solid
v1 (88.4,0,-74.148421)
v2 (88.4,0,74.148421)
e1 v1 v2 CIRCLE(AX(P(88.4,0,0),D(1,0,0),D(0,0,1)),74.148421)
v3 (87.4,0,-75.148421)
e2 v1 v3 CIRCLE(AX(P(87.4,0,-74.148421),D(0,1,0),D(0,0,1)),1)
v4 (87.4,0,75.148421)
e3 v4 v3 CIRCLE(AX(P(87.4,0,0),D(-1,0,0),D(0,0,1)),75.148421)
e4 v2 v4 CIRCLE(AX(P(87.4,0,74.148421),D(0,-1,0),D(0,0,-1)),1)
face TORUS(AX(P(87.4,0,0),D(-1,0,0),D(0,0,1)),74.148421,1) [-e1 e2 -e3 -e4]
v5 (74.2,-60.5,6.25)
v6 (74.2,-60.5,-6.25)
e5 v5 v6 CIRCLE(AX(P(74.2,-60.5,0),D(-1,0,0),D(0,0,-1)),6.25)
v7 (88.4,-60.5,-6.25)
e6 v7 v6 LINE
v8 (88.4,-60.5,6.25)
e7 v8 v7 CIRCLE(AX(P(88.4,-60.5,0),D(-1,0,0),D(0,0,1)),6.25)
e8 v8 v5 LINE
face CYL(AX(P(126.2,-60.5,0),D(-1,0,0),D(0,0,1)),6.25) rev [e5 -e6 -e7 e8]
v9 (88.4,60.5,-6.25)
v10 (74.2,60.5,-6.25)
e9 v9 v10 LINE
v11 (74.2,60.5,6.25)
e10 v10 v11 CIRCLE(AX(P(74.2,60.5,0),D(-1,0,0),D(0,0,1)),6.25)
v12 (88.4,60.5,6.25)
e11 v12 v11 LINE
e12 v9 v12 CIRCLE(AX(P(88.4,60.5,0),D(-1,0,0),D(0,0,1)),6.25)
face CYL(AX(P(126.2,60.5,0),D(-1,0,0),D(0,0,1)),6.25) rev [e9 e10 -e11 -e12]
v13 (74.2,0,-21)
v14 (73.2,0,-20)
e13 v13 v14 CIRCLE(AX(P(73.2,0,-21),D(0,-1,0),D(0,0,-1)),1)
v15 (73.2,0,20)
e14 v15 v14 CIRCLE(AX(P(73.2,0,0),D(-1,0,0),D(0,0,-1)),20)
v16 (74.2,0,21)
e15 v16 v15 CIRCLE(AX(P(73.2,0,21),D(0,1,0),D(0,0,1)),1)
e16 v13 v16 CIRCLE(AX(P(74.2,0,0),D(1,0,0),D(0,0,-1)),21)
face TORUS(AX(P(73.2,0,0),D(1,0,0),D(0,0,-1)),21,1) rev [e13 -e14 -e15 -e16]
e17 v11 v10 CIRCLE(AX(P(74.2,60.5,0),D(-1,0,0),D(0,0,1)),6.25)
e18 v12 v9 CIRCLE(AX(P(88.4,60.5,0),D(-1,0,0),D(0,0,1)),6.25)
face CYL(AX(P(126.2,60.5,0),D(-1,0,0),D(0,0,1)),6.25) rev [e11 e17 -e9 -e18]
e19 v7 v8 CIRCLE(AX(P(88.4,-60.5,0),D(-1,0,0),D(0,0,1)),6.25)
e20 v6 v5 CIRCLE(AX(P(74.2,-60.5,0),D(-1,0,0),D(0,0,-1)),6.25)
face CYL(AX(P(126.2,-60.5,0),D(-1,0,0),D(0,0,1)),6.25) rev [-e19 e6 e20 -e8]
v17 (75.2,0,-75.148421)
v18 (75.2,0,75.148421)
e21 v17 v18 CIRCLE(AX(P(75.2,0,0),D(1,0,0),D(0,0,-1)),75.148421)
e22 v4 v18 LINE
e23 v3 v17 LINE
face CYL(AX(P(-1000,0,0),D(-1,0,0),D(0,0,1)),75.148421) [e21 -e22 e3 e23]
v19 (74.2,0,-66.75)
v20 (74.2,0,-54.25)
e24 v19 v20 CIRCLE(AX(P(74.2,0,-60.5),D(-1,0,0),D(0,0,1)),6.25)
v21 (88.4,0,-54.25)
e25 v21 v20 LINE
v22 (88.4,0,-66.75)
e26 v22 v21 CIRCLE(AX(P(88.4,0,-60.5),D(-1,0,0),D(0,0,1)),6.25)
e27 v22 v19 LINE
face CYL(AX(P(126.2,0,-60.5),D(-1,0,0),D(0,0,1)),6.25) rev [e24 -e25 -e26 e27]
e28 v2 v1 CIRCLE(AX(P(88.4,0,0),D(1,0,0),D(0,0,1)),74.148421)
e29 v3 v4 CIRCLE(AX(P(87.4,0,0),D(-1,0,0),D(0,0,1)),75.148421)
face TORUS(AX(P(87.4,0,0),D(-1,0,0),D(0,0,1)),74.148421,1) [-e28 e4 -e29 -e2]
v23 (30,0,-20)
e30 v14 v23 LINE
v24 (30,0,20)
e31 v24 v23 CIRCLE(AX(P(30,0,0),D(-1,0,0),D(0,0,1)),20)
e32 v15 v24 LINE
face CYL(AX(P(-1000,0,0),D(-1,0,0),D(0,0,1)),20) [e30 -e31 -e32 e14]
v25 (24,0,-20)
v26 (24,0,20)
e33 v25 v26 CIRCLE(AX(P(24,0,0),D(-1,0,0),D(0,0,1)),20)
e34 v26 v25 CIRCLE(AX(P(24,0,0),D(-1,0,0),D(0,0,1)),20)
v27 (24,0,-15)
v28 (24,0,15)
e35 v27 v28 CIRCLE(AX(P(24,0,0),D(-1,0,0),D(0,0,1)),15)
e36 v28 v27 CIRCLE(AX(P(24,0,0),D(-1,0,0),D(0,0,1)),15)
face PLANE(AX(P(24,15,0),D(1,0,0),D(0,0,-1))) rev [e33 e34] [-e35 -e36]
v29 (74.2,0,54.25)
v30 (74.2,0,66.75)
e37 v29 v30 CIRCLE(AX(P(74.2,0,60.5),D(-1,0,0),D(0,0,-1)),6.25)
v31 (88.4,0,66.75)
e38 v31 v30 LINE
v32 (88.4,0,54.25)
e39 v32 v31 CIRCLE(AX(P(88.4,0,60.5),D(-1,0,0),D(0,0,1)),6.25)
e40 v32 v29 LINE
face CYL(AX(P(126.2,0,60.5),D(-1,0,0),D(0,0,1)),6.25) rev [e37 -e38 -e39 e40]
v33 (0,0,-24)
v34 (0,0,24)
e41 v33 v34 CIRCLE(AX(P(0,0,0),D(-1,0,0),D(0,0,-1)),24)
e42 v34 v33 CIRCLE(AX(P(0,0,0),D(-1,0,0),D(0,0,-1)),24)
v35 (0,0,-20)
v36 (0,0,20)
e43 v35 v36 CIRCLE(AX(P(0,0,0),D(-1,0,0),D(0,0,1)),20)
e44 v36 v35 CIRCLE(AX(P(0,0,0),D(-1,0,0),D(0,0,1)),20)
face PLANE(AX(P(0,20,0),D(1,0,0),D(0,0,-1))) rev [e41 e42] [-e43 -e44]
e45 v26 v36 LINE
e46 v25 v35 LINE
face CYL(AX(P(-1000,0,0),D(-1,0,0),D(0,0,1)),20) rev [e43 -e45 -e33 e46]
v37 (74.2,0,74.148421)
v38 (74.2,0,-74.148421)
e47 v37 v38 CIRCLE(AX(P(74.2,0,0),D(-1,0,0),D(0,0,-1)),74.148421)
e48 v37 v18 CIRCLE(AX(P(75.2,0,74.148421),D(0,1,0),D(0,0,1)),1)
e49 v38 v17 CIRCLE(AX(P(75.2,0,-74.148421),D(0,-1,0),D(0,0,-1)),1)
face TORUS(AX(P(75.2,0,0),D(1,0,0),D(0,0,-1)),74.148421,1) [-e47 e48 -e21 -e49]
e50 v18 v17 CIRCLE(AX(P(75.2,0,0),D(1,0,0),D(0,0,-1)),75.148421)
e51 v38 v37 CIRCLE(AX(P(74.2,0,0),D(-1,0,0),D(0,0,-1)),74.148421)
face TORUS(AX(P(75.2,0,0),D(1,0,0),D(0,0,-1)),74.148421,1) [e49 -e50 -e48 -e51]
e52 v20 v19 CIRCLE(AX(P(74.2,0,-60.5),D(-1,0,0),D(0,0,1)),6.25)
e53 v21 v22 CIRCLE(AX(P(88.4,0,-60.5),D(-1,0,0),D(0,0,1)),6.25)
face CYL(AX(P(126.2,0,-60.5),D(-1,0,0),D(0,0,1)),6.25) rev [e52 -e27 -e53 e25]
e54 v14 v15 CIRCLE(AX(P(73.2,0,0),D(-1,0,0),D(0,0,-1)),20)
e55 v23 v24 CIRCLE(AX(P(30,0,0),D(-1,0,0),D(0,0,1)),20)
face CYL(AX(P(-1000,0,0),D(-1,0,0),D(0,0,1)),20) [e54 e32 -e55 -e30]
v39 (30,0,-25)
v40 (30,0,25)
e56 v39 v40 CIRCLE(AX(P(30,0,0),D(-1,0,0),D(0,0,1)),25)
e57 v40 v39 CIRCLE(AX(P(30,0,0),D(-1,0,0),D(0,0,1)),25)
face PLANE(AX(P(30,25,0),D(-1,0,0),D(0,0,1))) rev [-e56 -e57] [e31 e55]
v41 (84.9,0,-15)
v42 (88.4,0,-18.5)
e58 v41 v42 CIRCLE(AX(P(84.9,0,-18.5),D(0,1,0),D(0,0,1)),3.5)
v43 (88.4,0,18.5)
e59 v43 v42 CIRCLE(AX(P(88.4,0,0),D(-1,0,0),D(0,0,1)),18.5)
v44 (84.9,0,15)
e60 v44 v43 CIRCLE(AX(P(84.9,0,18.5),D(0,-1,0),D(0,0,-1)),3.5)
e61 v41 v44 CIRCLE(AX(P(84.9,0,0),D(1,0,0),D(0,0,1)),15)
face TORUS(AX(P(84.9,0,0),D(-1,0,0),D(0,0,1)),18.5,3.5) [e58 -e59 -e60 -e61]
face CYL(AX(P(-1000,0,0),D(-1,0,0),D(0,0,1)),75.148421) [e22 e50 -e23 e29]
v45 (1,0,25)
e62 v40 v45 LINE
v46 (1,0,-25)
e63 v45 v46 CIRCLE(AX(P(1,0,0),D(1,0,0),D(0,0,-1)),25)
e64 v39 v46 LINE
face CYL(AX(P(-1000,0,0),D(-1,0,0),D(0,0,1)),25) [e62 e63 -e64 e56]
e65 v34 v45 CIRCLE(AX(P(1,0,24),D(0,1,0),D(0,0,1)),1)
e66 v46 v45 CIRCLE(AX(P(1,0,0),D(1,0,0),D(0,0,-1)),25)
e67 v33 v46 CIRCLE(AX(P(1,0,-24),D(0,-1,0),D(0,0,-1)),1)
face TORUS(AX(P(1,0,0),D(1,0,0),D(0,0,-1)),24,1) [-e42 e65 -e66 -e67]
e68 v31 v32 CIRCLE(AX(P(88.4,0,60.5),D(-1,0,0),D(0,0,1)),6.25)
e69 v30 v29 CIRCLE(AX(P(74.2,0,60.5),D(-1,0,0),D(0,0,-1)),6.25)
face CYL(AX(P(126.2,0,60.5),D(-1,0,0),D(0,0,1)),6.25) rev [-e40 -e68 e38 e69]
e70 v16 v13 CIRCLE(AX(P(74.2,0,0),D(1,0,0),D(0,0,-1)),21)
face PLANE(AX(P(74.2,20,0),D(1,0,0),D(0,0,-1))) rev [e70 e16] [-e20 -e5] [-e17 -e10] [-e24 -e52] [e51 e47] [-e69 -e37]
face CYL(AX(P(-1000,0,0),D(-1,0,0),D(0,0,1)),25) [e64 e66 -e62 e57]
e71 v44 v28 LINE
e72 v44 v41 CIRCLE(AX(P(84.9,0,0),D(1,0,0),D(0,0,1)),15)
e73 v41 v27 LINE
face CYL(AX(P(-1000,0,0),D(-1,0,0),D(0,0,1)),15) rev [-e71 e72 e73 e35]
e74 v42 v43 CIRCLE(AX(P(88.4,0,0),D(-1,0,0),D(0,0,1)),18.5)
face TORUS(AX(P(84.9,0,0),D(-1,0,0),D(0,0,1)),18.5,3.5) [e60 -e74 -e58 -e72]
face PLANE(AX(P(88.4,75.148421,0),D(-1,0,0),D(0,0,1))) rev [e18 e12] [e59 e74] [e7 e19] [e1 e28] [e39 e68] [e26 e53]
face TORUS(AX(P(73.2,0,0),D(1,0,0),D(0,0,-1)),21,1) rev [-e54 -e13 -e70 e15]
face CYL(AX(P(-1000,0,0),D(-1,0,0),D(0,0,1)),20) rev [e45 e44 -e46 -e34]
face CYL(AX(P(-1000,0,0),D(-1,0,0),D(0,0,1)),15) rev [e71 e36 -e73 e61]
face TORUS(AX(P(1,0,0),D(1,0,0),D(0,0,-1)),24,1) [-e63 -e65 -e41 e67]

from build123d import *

# Parameters (mm, degrees)
BOLT_HOLES_SKETCH_R        = 6.25
FLANGE_BOLT_HOLES_4X_DEPTH = 52
FILLET_R3_5_R              = 3.5
FILLET_R1_R                = 1


with BuildPart() as part:
    # Connector Profile Sketch → Connector Body Revolve (revolve)
    with BuildSketch(Plane.XY, mode=Mode.PRIVATE) as connector_body_revolve_sk:
        Polygon((0, 25), (30, 25), (30, 20), (74.2, 20), (74.2, 75.14842088), (88.4, 75.14842088), (88.4, 15), (24, 15), (24, 20), (0, 20), align=None)
    revolve(connector_body_revolve_sk.sketch.rotate(Axis((-1000, 0, 0), (1, 0, 0)), 90), axis=Axis((-1000, 0, 0), (1, 0, 0)))

    # Bolt Holes Sketch → Flange Bolt Holes 4x (cut)
    with BuildSketch(Plane.ZY.offset(-74.2)):
        with Locations((0, 60.5)):
            Circle(BOLT_HOLES_SKETCH_R)
        with Locations((0, -60.5)):
            Circle(BOLT_HOLES_SKETCH_R)
        with Locations((-60.5, 0)):
            Circle(BOLT_HOLES_SKETCH_R)
        with Locations((60.5, 0)):
            Circle(BOLT_HOLES_SKETCH_R)
    extrude(amount=-FLANGE_BOLT_HOLES_4X_DEPTH, mode=Mode.SUBTRACT)

    # Fillet R3.5
    fillet_r3_5_edges = [part.edges().sort_by_distance(p)[0] for p in [
        (88.4, 0, -15),
    ]]
    fillet(fillet_r3_5_edges, radius=FILLET_R3_5_R)

    # Fillet R1
    fillet_r1_edges = [part.edges().sort_by_distance(p)[0] for p in [
        (74.2, 0, -75.14842088),
        (74.2, 0, -20),
        (0, 0, -25),
        (88.4, 0, -75.14842088),
    ]]
    fillet(fillet_r1_edges, radius=FILLET_R1_R)


solid = part.part
